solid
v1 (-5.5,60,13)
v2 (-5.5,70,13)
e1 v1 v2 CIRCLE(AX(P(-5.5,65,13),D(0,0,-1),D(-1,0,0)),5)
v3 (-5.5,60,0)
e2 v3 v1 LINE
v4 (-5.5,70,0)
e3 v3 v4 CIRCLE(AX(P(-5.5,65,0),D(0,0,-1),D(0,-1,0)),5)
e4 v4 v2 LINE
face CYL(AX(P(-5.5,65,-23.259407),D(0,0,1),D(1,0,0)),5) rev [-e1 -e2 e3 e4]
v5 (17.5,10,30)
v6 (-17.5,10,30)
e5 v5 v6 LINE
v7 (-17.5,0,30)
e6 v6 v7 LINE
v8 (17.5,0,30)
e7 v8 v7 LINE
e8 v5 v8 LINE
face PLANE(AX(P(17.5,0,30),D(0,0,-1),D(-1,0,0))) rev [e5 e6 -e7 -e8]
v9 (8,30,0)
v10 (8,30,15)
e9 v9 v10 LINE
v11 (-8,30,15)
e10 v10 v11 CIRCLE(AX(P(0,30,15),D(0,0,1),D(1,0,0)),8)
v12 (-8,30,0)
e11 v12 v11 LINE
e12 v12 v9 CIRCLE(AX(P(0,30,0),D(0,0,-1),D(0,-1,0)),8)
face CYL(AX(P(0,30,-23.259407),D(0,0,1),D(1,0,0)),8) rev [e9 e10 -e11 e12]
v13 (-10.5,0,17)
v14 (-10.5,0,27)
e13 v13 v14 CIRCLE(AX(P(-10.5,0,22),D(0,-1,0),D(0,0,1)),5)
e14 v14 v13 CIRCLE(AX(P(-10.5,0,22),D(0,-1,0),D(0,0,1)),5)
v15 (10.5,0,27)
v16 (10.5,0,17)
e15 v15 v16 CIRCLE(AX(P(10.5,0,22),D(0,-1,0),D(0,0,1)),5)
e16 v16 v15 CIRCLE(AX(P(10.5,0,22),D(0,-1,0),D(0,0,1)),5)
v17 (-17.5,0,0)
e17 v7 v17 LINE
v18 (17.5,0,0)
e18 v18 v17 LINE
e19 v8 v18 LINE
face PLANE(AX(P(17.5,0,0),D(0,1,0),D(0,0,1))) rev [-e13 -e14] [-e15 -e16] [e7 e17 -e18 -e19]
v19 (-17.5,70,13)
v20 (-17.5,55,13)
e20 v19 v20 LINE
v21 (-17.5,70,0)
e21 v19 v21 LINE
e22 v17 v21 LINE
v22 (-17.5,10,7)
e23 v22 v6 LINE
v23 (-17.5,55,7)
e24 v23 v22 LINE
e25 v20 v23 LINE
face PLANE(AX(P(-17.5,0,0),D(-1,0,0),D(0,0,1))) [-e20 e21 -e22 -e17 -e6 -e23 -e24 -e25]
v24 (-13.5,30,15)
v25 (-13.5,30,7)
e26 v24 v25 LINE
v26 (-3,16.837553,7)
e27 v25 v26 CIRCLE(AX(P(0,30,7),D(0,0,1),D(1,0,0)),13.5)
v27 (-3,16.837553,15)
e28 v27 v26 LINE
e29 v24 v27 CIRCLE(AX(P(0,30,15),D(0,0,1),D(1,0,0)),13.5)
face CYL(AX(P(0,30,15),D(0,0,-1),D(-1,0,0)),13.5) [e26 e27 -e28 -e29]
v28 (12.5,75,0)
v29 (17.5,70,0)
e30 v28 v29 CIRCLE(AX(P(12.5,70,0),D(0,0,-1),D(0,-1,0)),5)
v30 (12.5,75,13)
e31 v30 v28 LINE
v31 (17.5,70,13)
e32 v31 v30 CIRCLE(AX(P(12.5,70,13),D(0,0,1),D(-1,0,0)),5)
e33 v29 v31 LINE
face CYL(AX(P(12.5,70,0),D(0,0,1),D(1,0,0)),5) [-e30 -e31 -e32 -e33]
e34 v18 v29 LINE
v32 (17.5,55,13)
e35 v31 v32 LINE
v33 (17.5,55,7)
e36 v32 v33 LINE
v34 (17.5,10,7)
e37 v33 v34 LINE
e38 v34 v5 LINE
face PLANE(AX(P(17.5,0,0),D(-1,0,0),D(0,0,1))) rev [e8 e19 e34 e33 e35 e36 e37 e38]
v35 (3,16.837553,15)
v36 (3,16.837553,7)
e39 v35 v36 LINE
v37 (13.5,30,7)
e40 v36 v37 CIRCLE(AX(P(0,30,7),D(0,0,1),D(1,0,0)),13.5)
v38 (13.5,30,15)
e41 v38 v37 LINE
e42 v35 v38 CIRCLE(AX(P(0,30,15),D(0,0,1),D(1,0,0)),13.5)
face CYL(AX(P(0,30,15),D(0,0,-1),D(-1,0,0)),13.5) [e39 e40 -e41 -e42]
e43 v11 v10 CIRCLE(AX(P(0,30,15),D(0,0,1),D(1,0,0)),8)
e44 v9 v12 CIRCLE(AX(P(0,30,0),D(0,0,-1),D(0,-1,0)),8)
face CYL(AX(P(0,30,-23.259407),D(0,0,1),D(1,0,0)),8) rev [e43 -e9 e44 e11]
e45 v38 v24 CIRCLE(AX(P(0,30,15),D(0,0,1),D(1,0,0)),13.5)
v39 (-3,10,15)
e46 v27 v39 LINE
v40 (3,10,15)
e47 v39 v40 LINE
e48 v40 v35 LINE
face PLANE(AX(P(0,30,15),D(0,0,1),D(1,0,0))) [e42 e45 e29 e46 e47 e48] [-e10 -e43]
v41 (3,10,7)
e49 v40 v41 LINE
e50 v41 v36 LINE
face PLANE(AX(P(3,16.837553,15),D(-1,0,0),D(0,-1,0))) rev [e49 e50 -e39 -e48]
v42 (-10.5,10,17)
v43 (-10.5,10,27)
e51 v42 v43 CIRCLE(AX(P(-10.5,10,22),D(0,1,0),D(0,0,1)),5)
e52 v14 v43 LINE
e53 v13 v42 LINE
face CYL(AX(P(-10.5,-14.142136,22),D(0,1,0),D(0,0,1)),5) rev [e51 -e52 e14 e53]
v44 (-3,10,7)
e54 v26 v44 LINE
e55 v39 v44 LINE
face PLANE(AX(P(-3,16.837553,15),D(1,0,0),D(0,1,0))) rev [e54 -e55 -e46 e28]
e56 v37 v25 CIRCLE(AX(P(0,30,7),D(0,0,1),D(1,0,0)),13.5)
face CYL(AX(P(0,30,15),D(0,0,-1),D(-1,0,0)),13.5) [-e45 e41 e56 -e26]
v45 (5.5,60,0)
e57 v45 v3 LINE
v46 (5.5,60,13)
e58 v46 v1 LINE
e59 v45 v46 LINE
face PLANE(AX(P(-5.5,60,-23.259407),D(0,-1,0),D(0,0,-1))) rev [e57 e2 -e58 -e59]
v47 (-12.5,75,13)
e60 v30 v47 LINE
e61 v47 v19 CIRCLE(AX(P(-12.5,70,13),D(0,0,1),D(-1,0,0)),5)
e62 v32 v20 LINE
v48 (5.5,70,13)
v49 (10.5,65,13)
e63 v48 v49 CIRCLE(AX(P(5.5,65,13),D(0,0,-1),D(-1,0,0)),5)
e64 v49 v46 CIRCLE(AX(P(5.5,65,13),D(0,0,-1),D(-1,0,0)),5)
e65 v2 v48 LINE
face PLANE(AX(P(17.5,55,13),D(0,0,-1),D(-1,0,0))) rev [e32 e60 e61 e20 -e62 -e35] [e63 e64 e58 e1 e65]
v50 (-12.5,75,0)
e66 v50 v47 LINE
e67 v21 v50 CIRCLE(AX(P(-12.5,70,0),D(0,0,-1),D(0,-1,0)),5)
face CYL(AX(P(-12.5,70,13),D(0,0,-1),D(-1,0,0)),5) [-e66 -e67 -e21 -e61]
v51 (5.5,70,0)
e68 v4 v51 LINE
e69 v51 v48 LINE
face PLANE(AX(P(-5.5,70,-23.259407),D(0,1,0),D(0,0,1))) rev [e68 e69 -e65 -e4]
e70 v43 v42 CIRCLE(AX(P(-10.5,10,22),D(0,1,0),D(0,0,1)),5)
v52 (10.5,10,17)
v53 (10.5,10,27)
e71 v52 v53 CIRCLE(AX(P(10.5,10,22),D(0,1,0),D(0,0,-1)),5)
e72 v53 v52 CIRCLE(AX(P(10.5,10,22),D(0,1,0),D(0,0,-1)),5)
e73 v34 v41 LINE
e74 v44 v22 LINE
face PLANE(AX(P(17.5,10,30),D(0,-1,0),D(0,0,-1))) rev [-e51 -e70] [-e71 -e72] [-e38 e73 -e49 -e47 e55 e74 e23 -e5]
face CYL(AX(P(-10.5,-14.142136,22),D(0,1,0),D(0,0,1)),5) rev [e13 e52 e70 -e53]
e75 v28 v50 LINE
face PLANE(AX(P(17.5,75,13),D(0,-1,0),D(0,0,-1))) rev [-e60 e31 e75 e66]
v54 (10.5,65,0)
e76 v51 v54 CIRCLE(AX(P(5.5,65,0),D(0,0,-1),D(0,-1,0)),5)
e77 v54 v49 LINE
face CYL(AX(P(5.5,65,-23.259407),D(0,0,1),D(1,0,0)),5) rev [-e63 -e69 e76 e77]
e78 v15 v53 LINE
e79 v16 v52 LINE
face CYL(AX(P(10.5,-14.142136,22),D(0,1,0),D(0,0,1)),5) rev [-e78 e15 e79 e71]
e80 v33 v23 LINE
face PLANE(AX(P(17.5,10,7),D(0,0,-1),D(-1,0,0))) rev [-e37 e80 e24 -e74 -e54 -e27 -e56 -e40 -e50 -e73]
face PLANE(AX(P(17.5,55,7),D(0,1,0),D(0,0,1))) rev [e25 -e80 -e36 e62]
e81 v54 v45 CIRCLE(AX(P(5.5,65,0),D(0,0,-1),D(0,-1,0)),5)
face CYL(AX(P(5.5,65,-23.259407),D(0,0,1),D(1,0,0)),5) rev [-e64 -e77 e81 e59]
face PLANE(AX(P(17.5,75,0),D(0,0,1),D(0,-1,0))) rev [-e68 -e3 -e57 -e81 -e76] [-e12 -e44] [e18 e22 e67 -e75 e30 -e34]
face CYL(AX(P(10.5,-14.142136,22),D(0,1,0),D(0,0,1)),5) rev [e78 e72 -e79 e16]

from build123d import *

# Parameters (mm, degrees)
L_BRACKET_BODY_DEPTH        = 17.5
TOP_CORNER_FILLET_R5_R      = 5
BORE_BOSS_DEPTH             = 8
BORE_AND_SLOT_SKETCH_R      = 8
BORE_AND_TOP_SLOT_CUT_DEPTH = 15
BASE_HOLES_SKETCH_R         = 5
BASE_MOUNTING_HOLES_DEPTH   = 10


with BuildPart() as part:
    # L Profile Sketch → L Bracket Body (new, symmetric)
    with BuildSketch(Plane(origin=(0, 0, 0), x_dir=(0, 0, -1), z_dir=(1, 0, 0))):
        Polygon((0, 0), (-30, 0), (-30, 10), (-7, 10), (-7, 55), (-13, 55), (-13, 75), (0, 75), align=None)
    extrude(amount=L_BRACKET_BODY_DEPTH, both=True)

    # Top Corner Fillet R5
    top_corner_fillet_r5_edges = [part.edges().sort_by_distance(p)[0] for p in [
        (-17.5, 75, 6.5),
        (17.5, 75, 6.5),
    ]]
    fillet(top_corner_fillet_r5_edges, radius=TOP_CORNER_FILLET_R5_R)

    # Bore Boss Sketch → Bore Boss (add)
    with BuildSketch(Plane.XY.offset(7)):
        with BuildLine():
            Line((-3, 16.837553419), (-3, 10))
            Line((-3, 10), (3, 10))
            Line((3, 10), (3, 16.837553419))
            ThreePointArc((3, 16.837553419), (0, 43.5), (-3, 16.837553419))
        make_face()
    extrude(amount=BORE_BOSS_DEPTH)

    # Bore and Slot Sketch → Bore and Top Slot Cut (cut)
    with BuildSketch(Plane.XY.offset(15)):
        with Locations((0, 30)):
            Circle(BORE_AND_SLOT_SKETCH_R)
        with BuildLine():
            Line((-5.5, 70), (5.5, 70))
            ThreePointArc((5.5, 70), (10.5, 65), (5.5, 60))
            Line((5.5, 60), (-5.5, 60))
            ThreePointArc((-5.5, 60), (-10.5, 65), (-5.5, 70))
        make_face()
    extrude(amount=-BORE_AND_TOP_SLOT_CUT_DEPTH, mode=Mode.SUBTRACT)

    # Base Holes Sketch → Base Mounting Holes (cut)
    with BuildSketch(Plane(origin=(0, 10, 0), x_dir=(1, 0, 0), z_dir=(0, 1, 0))):
        with Locations(Location((-10.5, -22, 0), (0, 0, 270))):
            Circle(BASE_HOLES_SKETCH_R)
        with Locations(Location((10.5, -22, 0), (0, 0, 270))):
            Circle(BASE_HOLES_SKETCH_R)
    extrude(amount=-BASE_MOUNTING_HOLES_DEPTH, mode=Mode.SUBTRACT)


solid = part.part
